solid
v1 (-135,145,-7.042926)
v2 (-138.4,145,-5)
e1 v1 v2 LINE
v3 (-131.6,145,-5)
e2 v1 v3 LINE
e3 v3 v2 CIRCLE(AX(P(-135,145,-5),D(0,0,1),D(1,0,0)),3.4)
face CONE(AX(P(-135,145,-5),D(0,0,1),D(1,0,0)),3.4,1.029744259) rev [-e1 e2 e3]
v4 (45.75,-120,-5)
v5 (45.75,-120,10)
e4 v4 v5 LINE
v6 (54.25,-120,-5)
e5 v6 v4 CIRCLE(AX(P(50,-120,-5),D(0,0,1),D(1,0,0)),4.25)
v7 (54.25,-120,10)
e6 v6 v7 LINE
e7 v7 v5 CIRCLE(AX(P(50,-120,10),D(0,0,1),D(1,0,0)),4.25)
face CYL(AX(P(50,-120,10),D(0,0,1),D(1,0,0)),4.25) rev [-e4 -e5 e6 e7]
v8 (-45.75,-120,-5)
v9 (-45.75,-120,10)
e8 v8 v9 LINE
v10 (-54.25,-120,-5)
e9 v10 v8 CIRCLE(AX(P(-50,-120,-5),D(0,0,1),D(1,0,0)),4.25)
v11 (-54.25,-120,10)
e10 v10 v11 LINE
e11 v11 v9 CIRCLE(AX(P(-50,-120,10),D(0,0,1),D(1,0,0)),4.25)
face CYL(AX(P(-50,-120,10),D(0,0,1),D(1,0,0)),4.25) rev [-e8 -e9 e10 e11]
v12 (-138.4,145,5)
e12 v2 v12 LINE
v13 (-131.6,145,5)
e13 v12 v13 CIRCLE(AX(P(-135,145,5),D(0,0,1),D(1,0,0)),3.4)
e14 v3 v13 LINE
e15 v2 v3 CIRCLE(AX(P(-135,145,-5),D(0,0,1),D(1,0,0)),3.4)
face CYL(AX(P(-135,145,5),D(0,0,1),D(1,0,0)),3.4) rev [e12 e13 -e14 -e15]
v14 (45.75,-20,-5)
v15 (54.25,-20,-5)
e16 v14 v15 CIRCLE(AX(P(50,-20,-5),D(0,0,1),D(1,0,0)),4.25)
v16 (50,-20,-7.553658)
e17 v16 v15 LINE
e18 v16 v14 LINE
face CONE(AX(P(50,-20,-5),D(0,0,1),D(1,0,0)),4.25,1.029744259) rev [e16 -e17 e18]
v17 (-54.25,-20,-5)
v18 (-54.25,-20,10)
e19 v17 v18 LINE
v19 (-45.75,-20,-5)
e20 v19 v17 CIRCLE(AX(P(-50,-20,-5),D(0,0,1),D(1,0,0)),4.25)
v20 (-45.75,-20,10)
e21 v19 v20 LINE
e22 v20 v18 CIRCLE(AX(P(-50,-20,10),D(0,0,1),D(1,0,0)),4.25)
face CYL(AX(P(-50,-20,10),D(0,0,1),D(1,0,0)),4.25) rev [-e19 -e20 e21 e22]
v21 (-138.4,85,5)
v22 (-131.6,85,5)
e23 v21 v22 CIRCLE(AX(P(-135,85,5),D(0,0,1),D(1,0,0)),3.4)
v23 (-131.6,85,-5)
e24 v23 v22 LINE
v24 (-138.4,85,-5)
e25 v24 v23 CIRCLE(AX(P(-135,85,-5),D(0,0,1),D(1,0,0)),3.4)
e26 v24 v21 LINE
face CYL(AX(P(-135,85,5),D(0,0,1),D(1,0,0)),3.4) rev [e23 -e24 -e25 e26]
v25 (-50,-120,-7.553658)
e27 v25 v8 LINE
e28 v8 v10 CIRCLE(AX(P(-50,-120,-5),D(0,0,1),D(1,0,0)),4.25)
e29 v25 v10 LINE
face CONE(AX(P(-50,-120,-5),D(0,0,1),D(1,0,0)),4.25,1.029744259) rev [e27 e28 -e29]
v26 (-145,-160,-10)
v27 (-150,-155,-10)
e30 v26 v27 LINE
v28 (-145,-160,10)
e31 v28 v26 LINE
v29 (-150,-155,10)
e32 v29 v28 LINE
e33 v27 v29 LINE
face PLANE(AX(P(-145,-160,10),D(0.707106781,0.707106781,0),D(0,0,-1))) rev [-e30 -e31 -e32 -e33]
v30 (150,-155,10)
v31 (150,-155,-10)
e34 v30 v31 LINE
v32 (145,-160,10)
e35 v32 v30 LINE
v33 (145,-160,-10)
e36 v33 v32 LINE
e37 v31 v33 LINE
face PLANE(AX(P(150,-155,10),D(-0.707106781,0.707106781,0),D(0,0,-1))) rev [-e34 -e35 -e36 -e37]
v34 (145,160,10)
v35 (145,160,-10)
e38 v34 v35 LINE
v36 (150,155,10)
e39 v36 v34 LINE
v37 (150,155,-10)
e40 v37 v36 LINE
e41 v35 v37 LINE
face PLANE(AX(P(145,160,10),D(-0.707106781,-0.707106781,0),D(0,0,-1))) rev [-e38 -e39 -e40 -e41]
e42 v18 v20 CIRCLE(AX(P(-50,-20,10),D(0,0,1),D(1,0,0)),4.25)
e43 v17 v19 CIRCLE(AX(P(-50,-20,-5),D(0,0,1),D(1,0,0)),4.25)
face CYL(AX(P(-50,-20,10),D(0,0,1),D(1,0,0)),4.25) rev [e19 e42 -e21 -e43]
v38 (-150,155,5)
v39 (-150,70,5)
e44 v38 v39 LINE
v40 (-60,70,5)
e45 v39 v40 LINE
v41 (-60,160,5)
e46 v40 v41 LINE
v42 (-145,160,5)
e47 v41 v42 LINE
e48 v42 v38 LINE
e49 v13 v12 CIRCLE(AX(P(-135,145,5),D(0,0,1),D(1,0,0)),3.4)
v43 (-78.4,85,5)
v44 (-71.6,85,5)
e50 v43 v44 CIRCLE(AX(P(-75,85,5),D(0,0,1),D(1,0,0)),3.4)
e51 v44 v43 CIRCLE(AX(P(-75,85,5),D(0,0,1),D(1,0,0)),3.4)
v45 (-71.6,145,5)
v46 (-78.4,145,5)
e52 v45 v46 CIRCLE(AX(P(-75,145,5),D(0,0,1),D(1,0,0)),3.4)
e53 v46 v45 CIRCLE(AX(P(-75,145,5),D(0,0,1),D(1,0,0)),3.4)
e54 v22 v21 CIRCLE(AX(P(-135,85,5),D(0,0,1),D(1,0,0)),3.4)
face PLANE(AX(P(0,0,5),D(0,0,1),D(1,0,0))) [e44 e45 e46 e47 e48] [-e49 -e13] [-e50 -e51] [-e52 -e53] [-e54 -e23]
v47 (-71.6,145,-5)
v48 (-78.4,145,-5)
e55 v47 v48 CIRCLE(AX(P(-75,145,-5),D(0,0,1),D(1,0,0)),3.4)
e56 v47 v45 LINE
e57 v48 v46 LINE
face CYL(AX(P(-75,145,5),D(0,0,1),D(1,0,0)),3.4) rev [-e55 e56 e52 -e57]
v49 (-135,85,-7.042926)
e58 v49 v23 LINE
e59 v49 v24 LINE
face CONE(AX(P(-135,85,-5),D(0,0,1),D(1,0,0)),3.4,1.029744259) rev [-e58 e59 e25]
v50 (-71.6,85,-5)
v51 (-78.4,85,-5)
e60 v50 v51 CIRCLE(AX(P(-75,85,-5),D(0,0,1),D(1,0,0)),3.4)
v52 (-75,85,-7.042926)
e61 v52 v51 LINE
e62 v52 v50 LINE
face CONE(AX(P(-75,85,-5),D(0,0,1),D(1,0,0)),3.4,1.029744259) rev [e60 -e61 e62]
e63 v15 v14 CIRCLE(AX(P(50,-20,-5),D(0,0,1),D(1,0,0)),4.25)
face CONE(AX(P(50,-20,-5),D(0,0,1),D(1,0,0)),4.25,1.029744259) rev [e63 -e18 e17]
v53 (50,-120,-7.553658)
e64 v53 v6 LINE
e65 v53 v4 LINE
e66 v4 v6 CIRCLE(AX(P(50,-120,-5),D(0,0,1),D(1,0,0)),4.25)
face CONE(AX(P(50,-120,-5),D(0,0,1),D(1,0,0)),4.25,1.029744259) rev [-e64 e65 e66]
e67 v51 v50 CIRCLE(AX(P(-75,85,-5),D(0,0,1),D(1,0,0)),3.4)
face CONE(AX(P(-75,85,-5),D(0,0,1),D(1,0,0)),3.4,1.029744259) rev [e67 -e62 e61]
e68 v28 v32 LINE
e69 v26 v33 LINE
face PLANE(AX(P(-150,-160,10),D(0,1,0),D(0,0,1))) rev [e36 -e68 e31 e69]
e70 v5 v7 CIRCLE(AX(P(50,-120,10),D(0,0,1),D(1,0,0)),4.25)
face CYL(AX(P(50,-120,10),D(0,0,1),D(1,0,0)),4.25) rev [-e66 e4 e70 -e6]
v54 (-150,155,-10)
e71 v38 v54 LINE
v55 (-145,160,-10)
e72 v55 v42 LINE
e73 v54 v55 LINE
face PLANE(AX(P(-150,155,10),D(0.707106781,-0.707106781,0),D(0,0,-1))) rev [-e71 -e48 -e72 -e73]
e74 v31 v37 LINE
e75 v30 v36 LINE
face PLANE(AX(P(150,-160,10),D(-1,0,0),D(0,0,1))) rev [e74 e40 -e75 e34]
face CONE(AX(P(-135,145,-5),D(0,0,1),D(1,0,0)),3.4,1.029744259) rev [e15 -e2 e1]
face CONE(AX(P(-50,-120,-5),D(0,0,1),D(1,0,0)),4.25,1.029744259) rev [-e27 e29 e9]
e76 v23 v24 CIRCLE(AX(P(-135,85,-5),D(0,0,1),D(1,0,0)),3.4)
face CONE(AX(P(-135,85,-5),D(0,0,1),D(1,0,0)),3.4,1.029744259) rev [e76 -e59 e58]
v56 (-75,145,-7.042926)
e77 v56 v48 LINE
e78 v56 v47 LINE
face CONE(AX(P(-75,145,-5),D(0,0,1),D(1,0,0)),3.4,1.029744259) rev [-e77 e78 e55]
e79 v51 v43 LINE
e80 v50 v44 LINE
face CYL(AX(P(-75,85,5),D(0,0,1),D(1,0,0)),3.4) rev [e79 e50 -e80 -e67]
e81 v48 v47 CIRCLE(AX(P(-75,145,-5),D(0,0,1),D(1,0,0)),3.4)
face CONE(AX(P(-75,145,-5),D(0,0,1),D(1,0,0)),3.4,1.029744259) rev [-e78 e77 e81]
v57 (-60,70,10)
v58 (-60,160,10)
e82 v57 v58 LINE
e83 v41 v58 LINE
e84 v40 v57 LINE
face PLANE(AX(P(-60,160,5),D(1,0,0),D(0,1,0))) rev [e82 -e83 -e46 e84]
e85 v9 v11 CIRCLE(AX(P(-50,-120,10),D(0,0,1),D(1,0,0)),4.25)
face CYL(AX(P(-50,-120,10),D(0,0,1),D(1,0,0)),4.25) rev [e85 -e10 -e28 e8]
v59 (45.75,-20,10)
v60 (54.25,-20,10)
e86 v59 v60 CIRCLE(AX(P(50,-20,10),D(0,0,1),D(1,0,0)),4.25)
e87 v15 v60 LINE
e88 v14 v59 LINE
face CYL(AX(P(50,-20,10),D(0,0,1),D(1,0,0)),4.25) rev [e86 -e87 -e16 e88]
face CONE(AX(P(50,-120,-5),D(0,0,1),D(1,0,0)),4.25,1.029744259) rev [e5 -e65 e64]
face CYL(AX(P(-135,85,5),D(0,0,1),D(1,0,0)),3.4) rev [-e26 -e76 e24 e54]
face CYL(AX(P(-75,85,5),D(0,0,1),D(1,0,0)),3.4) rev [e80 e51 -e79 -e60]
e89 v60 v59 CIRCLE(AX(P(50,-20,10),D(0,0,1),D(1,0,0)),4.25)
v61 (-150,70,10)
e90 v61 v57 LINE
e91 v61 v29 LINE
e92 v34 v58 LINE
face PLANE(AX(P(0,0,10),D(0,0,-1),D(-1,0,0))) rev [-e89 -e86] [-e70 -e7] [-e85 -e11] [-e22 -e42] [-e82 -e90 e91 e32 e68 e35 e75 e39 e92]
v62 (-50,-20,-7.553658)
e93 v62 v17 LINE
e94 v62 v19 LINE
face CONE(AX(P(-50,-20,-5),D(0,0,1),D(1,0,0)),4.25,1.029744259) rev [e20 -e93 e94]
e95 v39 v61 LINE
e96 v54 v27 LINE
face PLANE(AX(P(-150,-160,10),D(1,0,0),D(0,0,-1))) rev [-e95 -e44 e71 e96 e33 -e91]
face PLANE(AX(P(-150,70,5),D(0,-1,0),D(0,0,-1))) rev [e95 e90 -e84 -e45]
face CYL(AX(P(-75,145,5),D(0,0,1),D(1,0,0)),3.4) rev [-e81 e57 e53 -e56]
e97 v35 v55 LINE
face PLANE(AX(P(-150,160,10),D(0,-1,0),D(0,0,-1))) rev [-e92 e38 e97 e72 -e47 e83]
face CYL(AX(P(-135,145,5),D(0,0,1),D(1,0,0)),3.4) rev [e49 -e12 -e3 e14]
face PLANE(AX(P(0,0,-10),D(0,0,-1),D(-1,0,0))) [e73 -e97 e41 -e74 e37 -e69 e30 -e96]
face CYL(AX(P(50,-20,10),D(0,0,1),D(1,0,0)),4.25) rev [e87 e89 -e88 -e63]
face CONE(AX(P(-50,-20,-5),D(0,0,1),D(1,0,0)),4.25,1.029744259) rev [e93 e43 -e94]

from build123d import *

# Parameters (mm, degrees)
SKETCH_1_W              = 300
SKETCH_1_H              = 320
EXTRUDE_1_DEPTH         = 10
HOLE_WIZARD_M10_1_D     = 8.5
HOLE_WIZARD_M10_1_DEPTH = 15
HOLE_WIZARD_M10_1_TIP   = 2.553657631
SKETCH_7_W              = 90
SKETCH_7_H              = 90
CUT_EXTRUDE_1_DEPTH     = 5
HOLE_WIZARD_M8_1_D      = 6.8
HOLE_WIZARD_M8_1_DEPTH  = 10
HOLE_WIZARD_M8_1_TIP    = 2.042926105
CHAMFER_1_SIZE          = 5


with BuildPart() as part:
    # 草图1 → 凸台-拉伸1 (new, symmetric)
    with BuildSketch(Plane.XY):
        Rectangle(SKETCH_1_W, SKETCH_1_H)
    extrude(amount=EXTRUDE_1_DEPTH, both=True)

    # M10 螺纹孔1
    with Locations(Plane.XY.offset(10)):
        with Locations((50, -20), (-50, -120), (-50, -20), (50, -120)):
            Hole(HOLE_WIZARD_M10_1_D / 2, depth=HOLE_WIZARD_M10_1_DEPTH)
            with Locations((0, 0, -(HOLE_WIZARD_M10_1_DEPTH + HOLE_WIZARD_M10_1_TIP / 2))):  # 118° drill point
                Cone(0, HOLE_WIZARD_M10_1_D / 2, HOLE_WIZARD_M10_1_TIP, mode=Mode.SUBTRACT)

    # 草图7 → 切除-拉伸1 (cut)
    with BuildSketch(Plane.XY.offset(10)):
        with Locations((-105, 115)):
            Rectangle(SKETCH_7_W, SKETCH_7_H)
    extrude(amount=-CUT_EXTRUDE_1_DEPTH, mode=Mode.SUBTRACT)

    # M8 螺纹孔1
    with Locations(Plane.XY.offset(5)):
        with Locations((-75, 85), (-75, 145), (-135, 85), (-135, 145)):
            Hole(HOLE_WIZARD_M8_1_D / 2, depth=HOLE_WIZARD_M8_1_DEPTH)
            with Locations((0, 0, -(HOLE_WIZARD_M8_1_DEPTH + HOLE_WIZARD_M8_1_TIP / 2))):  # 118° drill point
                Cone(0, HOLE_WIZARD_M8_1_D / 2, HOLE_WIZARD_M8_1_TIP, mode=Mode.SUBTRACT)

    # 倒角1
    chamfer_1_edges = [part.edges().sort_by_distance(p)[0] for p in [
        (-150, 160, -2.5),
        (150, -160, 0),
        (-150, -160, 0),
        (150, 160, 0),
    ]]
    chamfer(chamfer_1_edges, length=CHAMFER_1_SIZE)


solid = part.part
